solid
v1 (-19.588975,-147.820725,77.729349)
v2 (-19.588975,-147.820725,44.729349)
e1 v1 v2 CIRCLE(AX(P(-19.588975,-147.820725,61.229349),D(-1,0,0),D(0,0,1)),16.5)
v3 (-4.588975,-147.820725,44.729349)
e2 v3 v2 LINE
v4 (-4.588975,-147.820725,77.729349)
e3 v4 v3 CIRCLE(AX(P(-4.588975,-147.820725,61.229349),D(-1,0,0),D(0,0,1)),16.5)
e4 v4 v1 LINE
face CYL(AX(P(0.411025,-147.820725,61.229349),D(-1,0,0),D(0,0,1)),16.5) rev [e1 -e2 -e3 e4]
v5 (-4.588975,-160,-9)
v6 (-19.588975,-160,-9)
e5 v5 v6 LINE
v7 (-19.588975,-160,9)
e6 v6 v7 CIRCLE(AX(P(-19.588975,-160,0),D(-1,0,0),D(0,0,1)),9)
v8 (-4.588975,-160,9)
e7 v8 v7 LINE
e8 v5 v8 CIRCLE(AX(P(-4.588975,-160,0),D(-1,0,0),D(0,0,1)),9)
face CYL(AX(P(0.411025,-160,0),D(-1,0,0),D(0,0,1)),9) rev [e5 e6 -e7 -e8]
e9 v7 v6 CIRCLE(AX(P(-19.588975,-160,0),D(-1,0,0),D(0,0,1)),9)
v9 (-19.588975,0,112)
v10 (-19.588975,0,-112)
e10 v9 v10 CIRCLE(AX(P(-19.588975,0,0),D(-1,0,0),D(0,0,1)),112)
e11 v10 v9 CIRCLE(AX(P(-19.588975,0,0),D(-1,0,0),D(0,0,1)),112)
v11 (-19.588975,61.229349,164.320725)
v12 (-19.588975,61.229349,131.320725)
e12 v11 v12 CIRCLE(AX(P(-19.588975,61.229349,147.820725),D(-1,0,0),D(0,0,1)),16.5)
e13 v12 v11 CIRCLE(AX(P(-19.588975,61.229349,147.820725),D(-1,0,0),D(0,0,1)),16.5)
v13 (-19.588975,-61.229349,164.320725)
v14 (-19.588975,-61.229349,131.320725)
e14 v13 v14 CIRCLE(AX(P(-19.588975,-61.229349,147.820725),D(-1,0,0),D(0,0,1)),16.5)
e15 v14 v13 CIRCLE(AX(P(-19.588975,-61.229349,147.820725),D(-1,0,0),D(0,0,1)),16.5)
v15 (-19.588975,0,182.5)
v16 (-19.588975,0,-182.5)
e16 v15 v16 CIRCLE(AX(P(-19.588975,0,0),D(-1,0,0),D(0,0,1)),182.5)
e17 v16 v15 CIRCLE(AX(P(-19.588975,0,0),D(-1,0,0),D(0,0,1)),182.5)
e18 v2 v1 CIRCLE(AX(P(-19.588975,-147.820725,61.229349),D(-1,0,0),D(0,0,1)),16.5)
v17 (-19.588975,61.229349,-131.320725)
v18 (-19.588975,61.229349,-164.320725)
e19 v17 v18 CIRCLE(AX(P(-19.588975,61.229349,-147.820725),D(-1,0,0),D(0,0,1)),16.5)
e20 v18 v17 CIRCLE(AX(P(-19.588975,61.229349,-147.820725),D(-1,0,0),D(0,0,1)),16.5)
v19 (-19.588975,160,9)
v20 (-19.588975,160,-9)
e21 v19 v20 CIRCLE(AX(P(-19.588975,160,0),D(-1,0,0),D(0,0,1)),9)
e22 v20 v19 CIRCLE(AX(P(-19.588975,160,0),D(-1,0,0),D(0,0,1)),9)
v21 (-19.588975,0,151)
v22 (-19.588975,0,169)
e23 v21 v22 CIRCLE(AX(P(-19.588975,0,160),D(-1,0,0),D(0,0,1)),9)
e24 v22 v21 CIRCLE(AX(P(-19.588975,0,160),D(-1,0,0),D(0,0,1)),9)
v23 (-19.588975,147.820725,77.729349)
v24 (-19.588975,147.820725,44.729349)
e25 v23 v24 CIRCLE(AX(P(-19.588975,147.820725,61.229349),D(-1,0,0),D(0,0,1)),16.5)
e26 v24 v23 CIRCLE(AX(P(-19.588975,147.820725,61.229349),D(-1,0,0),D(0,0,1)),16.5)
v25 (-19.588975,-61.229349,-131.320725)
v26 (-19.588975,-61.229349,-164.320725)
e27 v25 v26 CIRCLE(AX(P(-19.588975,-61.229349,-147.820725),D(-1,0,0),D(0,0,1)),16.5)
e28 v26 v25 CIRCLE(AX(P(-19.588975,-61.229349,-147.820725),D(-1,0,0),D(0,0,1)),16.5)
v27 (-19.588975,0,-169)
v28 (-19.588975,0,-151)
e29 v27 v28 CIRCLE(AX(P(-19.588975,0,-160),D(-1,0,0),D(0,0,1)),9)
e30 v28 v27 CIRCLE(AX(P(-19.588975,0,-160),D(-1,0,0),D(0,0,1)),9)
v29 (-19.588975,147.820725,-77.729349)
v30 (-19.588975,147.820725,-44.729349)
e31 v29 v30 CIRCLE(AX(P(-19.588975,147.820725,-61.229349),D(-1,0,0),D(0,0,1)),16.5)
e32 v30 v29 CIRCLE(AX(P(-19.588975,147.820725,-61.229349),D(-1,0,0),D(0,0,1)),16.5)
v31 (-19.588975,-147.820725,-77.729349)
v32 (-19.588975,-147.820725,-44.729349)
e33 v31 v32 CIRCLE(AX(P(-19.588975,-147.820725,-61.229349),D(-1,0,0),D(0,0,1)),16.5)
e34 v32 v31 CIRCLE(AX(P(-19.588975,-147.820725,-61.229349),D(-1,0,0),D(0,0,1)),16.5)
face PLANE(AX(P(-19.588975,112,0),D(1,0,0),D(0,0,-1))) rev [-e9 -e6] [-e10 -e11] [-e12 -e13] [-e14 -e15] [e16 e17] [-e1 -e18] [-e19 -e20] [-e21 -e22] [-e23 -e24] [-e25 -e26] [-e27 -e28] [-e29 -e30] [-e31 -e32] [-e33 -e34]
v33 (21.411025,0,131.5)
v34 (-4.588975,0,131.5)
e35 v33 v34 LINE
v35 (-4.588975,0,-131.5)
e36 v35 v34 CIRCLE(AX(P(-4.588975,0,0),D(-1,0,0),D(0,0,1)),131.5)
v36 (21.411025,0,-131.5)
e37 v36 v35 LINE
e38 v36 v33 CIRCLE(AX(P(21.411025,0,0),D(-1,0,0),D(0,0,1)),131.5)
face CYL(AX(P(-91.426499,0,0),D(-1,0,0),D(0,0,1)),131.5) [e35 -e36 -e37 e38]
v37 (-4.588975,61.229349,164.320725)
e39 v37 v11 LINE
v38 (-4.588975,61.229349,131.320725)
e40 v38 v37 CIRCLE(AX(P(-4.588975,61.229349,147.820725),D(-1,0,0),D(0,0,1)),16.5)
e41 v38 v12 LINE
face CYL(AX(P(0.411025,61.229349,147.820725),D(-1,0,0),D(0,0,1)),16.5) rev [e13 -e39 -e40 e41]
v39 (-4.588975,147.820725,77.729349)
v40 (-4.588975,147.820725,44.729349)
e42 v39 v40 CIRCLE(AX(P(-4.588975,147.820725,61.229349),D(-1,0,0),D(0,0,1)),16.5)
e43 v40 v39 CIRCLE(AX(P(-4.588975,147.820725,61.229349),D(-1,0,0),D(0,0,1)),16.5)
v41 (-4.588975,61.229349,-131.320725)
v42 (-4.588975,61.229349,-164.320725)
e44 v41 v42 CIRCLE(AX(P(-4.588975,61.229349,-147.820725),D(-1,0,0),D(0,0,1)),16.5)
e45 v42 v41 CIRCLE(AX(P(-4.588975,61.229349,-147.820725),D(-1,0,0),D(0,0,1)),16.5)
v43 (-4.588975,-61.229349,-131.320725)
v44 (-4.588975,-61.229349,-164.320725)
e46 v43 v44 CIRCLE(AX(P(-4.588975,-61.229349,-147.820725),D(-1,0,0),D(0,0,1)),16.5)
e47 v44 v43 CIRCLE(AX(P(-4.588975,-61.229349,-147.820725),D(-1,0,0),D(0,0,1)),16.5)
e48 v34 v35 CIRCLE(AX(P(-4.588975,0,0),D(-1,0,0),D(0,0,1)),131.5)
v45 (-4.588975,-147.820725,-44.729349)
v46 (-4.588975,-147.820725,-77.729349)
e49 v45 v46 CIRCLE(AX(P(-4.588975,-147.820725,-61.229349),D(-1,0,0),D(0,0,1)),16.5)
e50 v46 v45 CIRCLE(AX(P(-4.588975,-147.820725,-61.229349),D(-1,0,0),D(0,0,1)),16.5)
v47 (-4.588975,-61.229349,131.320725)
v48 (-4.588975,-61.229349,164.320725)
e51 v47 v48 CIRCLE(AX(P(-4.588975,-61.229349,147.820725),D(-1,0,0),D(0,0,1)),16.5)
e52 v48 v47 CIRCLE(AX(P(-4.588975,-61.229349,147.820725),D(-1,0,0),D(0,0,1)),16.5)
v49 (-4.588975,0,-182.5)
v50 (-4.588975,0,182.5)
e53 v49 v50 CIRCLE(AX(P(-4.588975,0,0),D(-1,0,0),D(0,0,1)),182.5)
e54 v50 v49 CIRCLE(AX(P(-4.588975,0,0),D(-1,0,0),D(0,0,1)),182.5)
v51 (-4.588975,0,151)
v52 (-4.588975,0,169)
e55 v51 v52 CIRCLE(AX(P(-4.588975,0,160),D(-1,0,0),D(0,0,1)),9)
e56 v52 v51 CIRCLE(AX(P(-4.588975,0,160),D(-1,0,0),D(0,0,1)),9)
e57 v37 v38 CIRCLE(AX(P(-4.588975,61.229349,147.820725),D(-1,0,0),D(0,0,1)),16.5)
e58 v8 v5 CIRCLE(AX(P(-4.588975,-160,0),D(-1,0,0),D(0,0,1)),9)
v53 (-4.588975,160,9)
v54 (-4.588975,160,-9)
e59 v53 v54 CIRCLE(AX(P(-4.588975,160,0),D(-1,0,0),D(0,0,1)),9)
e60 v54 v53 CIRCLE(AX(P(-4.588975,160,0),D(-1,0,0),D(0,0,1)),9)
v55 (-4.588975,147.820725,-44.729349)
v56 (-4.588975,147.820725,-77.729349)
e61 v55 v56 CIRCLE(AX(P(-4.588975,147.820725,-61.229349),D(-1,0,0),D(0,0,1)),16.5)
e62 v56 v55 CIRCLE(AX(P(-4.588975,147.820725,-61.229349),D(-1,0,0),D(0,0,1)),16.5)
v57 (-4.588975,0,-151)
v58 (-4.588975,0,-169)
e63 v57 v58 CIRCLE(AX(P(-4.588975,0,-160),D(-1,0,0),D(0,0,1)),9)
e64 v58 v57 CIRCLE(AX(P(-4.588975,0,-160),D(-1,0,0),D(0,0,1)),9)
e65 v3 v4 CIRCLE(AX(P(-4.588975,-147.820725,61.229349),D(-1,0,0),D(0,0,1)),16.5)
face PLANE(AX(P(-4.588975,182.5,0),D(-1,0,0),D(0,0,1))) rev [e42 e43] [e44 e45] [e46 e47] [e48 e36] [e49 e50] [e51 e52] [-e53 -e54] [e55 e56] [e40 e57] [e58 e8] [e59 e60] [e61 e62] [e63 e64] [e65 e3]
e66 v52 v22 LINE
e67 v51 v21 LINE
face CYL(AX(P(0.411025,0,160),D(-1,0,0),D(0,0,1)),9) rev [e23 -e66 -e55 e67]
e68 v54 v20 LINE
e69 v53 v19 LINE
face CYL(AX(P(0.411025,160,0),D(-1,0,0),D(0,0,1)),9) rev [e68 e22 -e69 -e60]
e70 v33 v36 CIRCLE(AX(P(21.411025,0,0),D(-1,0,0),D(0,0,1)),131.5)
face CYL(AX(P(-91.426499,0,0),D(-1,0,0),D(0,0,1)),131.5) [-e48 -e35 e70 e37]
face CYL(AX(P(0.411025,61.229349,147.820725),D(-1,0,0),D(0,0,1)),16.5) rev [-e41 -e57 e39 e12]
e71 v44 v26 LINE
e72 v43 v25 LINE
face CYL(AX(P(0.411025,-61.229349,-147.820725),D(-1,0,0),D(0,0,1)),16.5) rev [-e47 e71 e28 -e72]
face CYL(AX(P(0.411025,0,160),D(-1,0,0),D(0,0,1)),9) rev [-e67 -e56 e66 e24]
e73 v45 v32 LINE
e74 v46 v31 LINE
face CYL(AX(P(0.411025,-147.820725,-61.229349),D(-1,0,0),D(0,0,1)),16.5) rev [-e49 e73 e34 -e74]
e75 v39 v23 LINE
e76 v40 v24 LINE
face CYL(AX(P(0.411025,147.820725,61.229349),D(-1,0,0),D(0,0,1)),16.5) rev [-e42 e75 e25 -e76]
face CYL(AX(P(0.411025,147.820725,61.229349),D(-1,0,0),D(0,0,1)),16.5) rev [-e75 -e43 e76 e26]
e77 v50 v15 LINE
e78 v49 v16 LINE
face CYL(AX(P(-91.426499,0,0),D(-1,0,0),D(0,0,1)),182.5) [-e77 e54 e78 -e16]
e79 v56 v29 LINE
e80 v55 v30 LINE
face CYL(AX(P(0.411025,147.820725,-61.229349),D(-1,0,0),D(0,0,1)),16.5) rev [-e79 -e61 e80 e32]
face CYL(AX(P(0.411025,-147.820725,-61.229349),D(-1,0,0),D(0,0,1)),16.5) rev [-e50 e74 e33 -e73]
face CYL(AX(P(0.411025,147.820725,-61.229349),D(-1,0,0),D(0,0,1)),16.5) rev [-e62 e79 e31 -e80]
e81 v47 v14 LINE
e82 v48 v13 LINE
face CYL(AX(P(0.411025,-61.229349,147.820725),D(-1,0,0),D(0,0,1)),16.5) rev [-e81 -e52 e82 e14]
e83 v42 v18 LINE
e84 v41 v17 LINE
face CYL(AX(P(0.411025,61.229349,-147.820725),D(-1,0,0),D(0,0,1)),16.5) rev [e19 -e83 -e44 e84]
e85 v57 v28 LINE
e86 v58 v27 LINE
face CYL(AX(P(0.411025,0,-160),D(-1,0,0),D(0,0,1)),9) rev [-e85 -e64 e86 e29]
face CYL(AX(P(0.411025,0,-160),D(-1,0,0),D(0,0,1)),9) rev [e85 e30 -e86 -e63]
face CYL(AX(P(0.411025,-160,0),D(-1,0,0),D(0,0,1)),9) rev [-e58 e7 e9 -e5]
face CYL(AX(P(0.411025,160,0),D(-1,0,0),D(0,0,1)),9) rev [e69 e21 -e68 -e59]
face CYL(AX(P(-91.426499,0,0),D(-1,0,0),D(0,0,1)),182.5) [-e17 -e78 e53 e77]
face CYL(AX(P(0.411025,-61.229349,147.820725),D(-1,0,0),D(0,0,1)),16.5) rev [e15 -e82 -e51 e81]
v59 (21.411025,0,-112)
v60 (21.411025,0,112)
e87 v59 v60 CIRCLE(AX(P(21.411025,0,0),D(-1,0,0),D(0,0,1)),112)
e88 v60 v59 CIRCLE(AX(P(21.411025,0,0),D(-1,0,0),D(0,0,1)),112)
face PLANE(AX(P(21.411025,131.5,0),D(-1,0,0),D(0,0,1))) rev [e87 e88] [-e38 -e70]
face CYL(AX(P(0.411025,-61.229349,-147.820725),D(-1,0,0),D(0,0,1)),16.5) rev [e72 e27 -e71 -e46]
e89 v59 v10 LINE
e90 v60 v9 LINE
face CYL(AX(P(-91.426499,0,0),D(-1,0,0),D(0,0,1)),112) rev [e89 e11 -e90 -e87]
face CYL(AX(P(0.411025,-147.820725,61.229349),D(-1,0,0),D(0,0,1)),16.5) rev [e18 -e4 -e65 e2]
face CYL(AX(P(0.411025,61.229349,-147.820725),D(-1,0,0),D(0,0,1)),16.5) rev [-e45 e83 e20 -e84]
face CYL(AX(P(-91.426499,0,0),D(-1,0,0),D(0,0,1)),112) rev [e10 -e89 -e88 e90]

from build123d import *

# Parameters (mm, degrees)
SKETCH2_R          = 16.5
CUT_EXTRUDE1_DEPTH = 20
SKETCH3_R          = 9
CUT_EXTRUDE2_DEPTH = 20


with BuildPart() as part:
    # Sketch1 → Revolve1 (revolve)
    with BuildSketch(Plane.XY, mode=Mode.PRIVATE) as revolve1_sk:
        Polygon((-19.588974855, 112), (-19.588974855, 182.5), (-4.588974855, 182.5), (-4.588974855, 131.5), (21.411025145, 131.5), (21.411025145, 112), align=None)
    revolve(revolve1_sk.sketch.rotate(Axis((-91.426499033, 0, 0), (1, 0, 0)), 90), axis=Axis((-91.426499033, 0, 0), (1, 0, 0)))

    # Sketch2 → Cut-Extrude1 (cut)
    with BuildSketch(Plane.ZY.offset(19.588974855)):
        with Locations((61.229349178, 147.820725202)):
            Circle(SKETCH2_R)
        with Locations((147.820725202, 61.229349178)):
            Circle(SKETCH2_R)
        with Locations((147.820725202, -61.229349178)):
            Circle(SKETCH2_R)
        with Locations((61.229349178, -147.820725202)):
            Circle(SKETCH2_R)
        with Locations((-61.229349178, -147.820725202)):
            Circle(SKETCH2_R)
        with Locations((-147.820725202, -61.229349178)):
            Circle(SKETCH2_R)
        with Locations((-147.820725202, 61.229349178)):
            Circle(SKETCH2_R)
        with Locations((-61.229349178, 147.820725202)):
            Circle(SKETCH2_R)
    extrude(amount=-CUT_EXTRUDE1_DEPTH, mode=Mode.SUBTRACT)

    # Sketch3 → Cut-Extrude2 (cut)
    with BuildSketch(Plane.ZY.offset(19.588974855)):
        with Locations((0, 160)):
            Circle(SKETCH3_R)
        with Locations((160, 0)):
            Circle(SKETCH3_R)
        with Locations((0, -160)):
            Circle(SKETCH3_R)
        with Locations((-160, 0)):
            Circle(SKETCH3_R)
    extrude(amount=-CUT_EXTRUDE2_DEPTH, mode=Mode.SUBTRACT)


solid = part.part
